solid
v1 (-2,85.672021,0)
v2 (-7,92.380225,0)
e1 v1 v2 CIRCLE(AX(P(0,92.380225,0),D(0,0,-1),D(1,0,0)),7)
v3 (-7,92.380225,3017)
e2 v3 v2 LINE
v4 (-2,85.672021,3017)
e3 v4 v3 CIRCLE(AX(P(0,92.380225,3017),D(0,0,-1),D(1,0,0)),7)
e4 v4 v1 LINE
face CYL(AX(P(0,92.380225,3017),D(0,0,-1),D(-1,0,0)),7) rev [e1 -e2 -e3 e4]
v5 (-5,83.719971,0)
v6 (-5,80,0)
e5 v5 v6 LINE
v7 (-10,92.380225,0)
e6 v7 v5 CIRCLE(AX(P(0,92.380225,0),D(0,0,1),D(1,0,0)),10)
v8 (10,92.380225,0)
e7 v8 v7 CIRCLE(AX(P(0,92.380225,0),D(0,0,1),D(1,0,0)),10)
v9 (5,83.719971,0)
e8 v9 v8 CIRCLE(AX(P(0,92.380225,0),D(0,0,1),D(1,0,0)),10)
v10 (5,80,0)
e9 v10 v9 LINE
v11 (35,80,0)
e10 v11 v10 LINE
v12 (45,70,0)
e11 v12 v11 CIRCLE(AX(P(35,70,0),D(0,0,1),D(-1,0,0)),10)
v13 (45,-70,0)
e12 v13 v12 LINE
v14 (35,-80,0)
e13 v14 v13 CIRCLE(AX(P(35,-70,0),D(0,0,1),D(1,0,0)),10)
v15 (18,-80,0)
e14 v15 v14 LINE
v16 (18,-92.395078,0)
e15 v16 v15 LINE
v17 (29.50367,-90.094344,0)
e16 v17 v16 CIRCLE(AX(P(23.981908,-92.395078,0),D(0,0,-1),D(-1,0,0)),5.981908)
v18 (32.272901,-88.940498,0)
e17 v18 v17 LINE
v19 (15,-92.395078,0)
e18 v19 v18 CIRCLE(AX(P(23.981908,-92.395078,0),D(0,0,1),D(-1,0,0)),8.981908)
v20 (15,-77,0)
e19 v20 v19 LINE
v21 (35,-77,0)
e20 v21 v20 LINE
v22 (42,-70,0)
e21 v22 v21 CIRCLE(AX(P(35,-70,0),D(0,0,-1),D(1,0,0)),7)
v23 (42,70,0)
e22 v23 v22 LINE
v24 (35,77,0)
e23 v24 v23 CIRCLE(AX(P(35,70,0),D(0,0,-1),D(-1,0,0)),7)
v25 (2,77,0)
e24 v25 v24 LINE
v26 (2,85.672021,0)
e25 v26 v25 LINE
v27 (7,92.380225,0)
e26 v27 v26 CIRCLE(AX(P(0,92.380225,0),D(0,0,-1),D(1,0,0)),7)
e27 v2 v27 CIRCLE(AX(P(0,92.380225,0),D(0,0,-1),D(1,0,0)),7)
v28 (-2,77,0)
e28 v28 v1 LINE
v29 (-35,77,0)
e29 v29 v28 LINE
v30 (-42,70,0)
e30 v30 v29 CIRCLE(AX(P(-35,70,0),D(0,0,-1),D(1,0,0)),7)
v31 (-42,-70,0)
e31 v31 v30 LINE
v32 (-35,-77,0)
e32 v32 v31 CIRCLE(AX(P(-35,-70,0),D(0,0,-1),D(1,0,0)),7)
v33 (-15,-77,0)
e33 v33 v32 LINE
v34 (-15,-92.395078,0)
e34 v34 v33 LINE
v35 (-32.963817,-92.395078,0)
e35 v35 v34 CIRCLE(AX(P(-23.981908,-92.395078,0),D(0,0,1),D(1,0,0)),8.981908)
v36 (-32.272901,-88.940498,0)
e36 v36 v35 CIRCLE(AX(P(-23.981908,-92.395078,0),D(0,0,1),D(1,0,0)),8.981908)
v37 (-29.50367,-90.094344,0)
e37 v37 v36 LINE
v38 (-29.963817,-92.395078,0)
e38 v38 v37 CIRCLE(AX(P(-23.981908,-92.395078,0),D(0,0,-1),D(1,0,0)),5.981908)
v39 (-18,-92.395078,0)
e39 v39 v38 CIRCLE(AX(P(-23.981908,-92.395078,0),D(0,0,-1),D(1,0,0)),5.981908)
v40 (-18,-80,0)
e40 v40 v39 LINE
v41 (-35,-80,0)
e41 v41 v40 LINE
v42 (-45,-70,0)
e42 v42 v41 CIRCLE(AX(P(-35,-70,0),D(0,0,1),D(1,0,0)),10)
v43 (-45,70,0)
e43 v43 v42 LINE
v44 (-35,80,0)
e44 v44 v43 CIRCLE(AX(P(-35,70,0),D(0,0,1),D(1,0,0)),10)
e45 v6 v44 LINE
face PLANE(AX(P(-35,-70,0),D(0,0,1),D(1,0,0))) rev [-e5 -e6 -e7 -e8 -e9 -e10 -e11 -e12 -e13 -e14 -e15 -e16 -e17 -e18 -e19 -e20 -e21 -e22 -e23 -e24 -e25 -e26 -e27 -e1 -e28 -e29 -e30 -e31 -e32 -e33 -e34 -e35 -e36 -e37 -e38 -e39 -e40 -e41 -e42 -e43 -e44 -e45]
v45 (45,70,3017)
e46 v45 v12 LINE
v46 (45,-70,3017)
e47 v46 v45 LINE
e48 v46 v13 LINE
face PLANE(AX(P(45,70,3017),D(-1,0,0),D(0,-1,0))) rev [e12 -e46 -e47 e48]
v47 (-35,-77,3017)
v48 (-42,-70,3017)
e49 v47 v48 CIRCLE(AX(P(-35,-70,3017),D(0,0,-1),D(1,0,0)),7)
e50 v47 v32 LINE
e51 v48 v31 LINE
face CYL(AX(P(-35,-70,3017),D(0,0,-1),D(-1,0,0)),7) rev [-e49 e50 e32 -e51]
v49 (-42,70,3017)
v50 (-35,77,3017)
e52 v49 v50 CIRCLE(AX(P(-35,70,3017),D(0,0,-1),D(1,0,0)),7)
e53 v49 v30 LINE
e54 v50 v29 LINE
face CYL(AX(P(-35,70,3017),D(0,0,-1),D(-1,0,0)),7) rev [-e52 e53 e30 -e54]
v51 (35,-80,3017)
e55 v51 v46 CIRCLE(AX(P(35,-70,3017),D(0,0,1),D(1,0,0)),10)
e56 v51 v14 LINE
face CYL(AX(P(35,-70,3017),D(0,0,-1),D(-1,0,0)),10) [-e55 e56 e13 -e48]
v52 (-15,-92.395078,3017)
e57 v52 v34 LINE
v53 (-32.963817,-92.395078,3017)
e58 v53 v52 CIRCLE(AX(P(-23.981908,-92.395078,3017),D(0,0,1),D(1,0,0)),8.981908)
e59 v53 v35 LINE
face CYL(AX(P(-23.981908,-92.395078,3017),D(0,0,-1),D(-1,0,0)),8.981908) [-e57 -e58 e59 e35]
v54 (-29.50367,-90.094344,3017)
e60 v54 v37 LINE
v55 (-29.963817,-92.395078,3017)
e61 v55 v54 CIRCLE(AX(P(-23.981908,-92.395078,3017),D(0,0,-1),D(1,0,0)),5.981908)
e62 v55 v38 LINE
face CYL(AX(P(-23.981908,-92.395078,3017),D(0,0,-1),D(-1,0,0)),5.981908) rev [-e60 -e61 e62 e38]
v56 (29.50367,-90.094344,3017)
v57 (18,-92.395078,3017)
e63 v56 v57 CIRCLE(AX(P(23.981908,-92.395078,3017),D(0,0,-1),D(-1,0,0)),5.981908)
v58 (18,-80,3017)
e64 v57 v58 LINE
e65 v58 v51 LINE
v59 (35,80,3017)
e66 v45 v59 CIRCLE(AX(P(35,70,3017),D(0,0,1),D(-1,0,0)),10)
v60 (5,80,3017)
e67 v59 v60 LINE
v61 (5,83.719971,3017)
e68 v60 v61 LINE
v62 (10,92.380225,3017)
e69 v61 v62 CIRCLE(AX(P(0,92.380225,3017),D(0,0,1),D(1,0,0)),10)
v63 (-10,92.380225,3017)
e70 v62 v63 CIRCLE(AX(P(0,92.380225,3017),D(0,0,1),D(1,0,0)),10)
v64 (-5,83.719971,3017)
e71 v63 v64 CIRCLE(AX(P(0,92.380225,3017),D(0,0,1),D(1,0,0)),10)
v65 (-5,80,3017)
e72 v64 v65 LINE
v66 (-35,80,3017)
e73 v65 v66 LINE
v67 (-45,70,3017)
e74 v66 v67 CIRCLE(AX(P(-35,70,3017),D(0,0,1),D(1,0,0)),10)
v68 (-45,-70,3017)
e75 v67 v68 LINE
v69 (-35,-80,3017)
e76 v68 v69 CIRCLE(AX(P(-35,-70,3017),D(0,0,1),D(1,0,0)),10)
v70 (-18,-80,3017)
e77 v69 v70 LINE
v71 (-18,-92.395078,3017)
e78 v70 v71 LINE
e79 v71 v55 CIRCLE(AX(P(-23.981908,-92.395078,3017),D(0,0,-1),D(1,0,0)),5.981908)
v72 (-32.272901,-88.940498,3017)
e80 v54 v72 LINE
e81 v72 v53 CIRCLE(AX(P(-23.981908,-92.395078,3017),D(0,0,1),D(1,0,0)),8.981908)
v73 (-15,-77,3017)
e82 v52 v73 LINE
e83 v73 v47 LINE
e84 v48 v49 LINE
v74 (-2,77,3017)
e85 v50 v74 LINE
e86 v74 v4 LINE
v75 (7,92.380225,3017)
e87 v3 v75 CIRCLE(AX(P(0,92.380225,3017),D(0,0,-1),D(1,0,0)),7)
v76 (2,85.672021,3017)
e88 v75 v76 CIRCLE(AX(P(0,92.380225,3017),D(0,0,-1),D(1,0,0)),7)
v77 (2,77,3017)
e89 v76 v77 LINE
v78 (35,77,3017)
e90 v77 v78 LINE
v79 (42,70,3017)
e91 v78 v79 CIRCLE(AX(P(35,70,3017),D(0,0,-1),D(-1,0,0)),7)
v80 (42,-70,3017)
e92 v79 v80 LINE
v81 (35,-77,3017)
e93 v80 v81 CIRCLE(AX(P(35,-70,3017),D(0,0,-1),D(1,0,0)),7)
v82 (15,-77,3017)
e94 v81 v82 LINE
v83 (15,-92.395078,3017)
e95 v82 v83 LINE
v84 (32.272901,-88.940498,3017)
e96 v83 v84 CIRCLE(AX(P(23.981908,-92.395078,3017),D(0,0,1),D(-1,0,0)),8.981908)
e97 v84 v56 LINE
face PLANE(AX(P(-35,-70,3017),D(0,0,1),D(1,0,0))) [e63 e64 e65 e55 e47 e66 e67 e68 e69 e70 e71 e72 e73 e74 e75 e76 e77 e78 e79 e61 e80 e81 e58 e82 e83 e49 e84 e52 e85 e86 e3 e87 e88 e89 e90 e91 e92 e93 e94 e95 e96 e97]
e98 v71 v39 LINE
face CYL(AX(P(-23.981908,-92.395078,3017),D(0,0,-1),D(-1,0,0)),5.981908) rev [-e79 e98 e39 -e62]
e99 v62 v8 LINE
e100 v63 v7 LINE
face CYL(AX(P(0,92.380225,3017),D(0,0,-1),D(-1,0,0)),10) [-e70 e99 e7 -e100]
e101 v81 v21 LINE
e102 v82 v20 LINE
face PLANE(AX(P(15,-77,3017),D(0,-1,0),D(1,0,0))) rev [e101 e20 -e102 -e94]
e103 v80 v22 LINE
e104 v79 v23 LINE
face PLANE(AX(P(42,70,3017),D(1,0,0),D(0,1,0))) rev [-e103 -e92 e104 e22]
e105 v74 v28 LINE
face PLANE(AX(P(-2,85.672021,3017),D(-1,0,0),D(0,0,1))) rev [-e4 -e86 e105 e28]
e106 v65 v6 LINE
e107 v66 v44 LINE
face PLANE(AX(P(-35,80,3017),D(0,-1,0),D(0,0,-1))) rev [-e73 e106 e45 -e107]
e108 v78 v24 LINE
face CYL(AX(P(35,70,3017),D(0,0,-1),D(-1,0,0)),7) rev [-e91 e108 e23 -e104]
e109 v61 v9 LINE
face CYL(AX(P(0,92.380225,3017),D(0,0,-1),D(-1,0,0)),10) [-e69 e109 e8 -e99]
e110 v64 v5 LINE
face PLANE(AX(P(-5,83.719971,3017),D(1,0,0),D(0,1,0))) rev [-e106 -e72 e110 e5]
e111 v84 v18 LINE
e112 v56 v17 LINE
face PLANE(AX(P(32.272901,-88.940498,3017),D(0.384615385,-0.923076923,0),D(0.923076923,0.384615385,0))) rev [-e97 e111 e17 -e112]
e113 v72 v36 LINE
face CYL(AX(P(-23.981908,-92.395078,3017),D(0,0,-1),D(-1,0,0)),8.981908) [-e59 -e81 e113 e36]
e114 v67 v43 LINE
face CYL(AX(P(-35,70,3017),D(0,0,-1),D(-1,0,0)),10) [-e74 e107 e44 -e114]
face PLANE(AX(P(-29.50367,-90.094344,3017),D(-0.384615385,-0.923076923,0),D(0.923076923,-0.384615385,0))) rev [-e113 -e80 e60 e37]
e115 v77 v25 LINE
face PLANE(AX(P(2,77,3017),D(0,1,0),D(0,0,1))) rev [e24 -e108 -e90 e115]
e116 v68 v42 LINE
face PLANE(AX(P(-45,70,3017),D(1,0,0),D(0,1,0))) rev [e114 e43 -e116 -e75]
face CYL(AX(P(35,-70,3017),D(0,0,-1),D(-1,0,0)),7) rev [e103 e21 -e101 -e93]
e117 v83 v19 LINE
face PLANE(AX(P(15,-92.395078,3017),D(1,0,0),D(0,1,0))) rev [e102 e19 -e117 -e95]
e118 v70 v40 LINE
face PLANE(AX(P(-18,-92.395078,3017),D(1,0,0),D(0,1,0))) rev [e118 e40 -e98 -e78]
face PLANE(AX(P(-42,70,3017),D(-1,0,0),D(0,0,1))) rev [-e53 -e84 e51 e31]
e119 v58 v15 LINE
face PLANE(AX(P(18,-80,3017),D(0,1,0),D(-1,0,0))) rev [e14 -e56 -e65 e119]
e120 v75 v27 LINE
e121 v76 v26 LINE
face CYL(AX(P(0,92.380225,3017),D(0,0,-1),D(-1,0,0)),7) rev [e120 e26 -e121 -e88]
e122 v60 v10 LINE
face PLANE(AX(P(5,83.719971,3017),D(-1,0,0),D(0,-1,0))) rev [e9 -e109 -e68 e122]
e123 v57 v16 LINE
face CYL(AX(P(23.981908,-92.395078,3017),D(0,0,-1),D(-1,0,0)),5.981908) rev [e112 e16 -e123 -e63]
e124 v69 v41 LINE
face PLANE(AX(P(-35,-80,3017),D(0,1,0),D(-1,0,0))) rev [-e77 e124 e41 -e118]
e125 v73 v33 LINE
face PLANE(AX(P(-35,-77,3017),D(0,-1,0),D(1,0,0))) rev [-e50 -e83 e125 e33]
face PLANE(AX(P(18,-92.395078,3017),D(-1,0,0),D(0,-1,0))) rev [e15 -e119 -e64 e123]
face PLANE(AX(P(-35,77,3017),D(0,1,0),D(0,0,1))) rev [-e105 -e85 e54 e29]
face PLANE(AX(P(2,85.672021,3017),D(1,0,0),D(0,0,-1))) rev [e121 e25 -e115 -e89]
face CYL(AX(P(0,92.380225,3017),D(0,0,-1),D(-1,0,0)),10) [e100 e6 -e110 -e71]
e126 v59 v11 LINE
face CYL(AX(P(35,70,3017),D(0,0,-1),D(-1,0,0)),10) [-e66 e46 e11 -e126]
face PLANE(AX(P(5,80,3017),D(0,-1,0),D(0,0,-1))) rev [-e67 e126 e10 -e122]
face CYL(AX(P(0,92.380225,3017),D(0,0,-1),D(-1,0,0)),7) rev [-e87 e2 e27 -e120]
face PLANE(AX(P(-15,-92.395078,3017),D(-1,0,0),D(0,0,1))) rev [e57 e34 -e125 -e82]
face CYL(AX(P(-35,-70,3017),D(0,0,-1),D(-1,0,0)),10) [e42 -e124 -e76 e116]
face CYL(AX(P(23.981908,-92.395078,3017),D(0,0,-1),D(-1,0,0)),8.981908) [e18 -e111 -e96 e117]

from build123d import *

# Parameters (mm, degrees)
BOSS_EXTRUDE1_DEPTH = 3017


with BuildPart() as part:
    # Sketch1 → Boss-Extrude1 (new body)
    with BuildSketch(Plane.XY):
        with BuildLine():
            Line((-35, 80), (-5, 80))
            Line((-5, 80), (-5, 83.719971064))
            ThreePointArc((-5, 83.719971064), (0, 102.380225102), (5, 83.719971064))
            Line((5, 83.719971064), (5, 80))
            Line((5, 80), (35, 80))
            ThreePointArc((35, 80), (42.071067812, 77.071067812), (45, 70))
            Line((45, 70), (45, -70))
            ThreePointArc((45, -70), (42.071067812, -77.071067812), (35, -80))
            Line((35, -80), (18, -80))
            Line((18, -80), (18, -92.395078412))
            ThreePointArc((18, -92.395078412), (25.155057115, -98.260822158), (29.503669933, -90.094344425))
            Line((29.503669933, -90.094344425), (32.272900703, -88.940498271))
            ThreePointArc((32.272900703, -88.940498271), (25.74340552, -101.202564185), (15, -92.395078412))
            Line((15, -92.395078412), (15, -77))
            Line((15, -77), (35, -77))
            ThreePointArc((35, -77), (39.949747468, -74.949747468), (42, -70))
            Line((42, -70), (42, 70))
            ThreePointArc((42, 70), (39.949747468, 74.949747468), (35, 77))
            Line((35, 77), (2, 77))
            Line((2, 77), (2, 85.672021169))
            ThreePointArc((2, 85.672021169), (0, 99.380225102), (-2, 85.672021169))
            Line((-2, 85.672021169), (-2, 77))
            Line((-2, 77), (-35, 77))
            ThreePointArc((-35, 77), (-39.949747468, 74.949747468), (-42, 70))
            Line((-42, 70), (-42, -70))
            ThreePointArc((-42, -70), (-39.949747468, -74.949747468), (-35, -77))
            Line((-35, -77), (-15, -77))
            Line((-15, -77), (-15, -92.395078412))
            ThreePointArc((-15, -92.395078412), (-25.74340552, -101.202564185), (-32.272900703, -88.940498271))
            Line((-32.272900703, -88.940498271), (-29.503669933, -90.094344425))
            ThreePointArc((-29.503669933, -90.094344425), (-25.155057115, -98.260822158), (-18, -92.395078412))
            Line((-18, -92.395078412), (-18, -80))
            Line((-18, -80), (-35, -80))
            ThreePointArc((-35, -80), (-42.071067812, -77.071067812), (-45, -70))
            Line((-45, -70), (-45, 70))
            ThreePointArc((-45, 70), (-42.071067812, 77.071067812), (-35, 80))
        make_face()
    extrude(amount=BOSS_EXTRUDE1_DEPTH)


solid = part.part
